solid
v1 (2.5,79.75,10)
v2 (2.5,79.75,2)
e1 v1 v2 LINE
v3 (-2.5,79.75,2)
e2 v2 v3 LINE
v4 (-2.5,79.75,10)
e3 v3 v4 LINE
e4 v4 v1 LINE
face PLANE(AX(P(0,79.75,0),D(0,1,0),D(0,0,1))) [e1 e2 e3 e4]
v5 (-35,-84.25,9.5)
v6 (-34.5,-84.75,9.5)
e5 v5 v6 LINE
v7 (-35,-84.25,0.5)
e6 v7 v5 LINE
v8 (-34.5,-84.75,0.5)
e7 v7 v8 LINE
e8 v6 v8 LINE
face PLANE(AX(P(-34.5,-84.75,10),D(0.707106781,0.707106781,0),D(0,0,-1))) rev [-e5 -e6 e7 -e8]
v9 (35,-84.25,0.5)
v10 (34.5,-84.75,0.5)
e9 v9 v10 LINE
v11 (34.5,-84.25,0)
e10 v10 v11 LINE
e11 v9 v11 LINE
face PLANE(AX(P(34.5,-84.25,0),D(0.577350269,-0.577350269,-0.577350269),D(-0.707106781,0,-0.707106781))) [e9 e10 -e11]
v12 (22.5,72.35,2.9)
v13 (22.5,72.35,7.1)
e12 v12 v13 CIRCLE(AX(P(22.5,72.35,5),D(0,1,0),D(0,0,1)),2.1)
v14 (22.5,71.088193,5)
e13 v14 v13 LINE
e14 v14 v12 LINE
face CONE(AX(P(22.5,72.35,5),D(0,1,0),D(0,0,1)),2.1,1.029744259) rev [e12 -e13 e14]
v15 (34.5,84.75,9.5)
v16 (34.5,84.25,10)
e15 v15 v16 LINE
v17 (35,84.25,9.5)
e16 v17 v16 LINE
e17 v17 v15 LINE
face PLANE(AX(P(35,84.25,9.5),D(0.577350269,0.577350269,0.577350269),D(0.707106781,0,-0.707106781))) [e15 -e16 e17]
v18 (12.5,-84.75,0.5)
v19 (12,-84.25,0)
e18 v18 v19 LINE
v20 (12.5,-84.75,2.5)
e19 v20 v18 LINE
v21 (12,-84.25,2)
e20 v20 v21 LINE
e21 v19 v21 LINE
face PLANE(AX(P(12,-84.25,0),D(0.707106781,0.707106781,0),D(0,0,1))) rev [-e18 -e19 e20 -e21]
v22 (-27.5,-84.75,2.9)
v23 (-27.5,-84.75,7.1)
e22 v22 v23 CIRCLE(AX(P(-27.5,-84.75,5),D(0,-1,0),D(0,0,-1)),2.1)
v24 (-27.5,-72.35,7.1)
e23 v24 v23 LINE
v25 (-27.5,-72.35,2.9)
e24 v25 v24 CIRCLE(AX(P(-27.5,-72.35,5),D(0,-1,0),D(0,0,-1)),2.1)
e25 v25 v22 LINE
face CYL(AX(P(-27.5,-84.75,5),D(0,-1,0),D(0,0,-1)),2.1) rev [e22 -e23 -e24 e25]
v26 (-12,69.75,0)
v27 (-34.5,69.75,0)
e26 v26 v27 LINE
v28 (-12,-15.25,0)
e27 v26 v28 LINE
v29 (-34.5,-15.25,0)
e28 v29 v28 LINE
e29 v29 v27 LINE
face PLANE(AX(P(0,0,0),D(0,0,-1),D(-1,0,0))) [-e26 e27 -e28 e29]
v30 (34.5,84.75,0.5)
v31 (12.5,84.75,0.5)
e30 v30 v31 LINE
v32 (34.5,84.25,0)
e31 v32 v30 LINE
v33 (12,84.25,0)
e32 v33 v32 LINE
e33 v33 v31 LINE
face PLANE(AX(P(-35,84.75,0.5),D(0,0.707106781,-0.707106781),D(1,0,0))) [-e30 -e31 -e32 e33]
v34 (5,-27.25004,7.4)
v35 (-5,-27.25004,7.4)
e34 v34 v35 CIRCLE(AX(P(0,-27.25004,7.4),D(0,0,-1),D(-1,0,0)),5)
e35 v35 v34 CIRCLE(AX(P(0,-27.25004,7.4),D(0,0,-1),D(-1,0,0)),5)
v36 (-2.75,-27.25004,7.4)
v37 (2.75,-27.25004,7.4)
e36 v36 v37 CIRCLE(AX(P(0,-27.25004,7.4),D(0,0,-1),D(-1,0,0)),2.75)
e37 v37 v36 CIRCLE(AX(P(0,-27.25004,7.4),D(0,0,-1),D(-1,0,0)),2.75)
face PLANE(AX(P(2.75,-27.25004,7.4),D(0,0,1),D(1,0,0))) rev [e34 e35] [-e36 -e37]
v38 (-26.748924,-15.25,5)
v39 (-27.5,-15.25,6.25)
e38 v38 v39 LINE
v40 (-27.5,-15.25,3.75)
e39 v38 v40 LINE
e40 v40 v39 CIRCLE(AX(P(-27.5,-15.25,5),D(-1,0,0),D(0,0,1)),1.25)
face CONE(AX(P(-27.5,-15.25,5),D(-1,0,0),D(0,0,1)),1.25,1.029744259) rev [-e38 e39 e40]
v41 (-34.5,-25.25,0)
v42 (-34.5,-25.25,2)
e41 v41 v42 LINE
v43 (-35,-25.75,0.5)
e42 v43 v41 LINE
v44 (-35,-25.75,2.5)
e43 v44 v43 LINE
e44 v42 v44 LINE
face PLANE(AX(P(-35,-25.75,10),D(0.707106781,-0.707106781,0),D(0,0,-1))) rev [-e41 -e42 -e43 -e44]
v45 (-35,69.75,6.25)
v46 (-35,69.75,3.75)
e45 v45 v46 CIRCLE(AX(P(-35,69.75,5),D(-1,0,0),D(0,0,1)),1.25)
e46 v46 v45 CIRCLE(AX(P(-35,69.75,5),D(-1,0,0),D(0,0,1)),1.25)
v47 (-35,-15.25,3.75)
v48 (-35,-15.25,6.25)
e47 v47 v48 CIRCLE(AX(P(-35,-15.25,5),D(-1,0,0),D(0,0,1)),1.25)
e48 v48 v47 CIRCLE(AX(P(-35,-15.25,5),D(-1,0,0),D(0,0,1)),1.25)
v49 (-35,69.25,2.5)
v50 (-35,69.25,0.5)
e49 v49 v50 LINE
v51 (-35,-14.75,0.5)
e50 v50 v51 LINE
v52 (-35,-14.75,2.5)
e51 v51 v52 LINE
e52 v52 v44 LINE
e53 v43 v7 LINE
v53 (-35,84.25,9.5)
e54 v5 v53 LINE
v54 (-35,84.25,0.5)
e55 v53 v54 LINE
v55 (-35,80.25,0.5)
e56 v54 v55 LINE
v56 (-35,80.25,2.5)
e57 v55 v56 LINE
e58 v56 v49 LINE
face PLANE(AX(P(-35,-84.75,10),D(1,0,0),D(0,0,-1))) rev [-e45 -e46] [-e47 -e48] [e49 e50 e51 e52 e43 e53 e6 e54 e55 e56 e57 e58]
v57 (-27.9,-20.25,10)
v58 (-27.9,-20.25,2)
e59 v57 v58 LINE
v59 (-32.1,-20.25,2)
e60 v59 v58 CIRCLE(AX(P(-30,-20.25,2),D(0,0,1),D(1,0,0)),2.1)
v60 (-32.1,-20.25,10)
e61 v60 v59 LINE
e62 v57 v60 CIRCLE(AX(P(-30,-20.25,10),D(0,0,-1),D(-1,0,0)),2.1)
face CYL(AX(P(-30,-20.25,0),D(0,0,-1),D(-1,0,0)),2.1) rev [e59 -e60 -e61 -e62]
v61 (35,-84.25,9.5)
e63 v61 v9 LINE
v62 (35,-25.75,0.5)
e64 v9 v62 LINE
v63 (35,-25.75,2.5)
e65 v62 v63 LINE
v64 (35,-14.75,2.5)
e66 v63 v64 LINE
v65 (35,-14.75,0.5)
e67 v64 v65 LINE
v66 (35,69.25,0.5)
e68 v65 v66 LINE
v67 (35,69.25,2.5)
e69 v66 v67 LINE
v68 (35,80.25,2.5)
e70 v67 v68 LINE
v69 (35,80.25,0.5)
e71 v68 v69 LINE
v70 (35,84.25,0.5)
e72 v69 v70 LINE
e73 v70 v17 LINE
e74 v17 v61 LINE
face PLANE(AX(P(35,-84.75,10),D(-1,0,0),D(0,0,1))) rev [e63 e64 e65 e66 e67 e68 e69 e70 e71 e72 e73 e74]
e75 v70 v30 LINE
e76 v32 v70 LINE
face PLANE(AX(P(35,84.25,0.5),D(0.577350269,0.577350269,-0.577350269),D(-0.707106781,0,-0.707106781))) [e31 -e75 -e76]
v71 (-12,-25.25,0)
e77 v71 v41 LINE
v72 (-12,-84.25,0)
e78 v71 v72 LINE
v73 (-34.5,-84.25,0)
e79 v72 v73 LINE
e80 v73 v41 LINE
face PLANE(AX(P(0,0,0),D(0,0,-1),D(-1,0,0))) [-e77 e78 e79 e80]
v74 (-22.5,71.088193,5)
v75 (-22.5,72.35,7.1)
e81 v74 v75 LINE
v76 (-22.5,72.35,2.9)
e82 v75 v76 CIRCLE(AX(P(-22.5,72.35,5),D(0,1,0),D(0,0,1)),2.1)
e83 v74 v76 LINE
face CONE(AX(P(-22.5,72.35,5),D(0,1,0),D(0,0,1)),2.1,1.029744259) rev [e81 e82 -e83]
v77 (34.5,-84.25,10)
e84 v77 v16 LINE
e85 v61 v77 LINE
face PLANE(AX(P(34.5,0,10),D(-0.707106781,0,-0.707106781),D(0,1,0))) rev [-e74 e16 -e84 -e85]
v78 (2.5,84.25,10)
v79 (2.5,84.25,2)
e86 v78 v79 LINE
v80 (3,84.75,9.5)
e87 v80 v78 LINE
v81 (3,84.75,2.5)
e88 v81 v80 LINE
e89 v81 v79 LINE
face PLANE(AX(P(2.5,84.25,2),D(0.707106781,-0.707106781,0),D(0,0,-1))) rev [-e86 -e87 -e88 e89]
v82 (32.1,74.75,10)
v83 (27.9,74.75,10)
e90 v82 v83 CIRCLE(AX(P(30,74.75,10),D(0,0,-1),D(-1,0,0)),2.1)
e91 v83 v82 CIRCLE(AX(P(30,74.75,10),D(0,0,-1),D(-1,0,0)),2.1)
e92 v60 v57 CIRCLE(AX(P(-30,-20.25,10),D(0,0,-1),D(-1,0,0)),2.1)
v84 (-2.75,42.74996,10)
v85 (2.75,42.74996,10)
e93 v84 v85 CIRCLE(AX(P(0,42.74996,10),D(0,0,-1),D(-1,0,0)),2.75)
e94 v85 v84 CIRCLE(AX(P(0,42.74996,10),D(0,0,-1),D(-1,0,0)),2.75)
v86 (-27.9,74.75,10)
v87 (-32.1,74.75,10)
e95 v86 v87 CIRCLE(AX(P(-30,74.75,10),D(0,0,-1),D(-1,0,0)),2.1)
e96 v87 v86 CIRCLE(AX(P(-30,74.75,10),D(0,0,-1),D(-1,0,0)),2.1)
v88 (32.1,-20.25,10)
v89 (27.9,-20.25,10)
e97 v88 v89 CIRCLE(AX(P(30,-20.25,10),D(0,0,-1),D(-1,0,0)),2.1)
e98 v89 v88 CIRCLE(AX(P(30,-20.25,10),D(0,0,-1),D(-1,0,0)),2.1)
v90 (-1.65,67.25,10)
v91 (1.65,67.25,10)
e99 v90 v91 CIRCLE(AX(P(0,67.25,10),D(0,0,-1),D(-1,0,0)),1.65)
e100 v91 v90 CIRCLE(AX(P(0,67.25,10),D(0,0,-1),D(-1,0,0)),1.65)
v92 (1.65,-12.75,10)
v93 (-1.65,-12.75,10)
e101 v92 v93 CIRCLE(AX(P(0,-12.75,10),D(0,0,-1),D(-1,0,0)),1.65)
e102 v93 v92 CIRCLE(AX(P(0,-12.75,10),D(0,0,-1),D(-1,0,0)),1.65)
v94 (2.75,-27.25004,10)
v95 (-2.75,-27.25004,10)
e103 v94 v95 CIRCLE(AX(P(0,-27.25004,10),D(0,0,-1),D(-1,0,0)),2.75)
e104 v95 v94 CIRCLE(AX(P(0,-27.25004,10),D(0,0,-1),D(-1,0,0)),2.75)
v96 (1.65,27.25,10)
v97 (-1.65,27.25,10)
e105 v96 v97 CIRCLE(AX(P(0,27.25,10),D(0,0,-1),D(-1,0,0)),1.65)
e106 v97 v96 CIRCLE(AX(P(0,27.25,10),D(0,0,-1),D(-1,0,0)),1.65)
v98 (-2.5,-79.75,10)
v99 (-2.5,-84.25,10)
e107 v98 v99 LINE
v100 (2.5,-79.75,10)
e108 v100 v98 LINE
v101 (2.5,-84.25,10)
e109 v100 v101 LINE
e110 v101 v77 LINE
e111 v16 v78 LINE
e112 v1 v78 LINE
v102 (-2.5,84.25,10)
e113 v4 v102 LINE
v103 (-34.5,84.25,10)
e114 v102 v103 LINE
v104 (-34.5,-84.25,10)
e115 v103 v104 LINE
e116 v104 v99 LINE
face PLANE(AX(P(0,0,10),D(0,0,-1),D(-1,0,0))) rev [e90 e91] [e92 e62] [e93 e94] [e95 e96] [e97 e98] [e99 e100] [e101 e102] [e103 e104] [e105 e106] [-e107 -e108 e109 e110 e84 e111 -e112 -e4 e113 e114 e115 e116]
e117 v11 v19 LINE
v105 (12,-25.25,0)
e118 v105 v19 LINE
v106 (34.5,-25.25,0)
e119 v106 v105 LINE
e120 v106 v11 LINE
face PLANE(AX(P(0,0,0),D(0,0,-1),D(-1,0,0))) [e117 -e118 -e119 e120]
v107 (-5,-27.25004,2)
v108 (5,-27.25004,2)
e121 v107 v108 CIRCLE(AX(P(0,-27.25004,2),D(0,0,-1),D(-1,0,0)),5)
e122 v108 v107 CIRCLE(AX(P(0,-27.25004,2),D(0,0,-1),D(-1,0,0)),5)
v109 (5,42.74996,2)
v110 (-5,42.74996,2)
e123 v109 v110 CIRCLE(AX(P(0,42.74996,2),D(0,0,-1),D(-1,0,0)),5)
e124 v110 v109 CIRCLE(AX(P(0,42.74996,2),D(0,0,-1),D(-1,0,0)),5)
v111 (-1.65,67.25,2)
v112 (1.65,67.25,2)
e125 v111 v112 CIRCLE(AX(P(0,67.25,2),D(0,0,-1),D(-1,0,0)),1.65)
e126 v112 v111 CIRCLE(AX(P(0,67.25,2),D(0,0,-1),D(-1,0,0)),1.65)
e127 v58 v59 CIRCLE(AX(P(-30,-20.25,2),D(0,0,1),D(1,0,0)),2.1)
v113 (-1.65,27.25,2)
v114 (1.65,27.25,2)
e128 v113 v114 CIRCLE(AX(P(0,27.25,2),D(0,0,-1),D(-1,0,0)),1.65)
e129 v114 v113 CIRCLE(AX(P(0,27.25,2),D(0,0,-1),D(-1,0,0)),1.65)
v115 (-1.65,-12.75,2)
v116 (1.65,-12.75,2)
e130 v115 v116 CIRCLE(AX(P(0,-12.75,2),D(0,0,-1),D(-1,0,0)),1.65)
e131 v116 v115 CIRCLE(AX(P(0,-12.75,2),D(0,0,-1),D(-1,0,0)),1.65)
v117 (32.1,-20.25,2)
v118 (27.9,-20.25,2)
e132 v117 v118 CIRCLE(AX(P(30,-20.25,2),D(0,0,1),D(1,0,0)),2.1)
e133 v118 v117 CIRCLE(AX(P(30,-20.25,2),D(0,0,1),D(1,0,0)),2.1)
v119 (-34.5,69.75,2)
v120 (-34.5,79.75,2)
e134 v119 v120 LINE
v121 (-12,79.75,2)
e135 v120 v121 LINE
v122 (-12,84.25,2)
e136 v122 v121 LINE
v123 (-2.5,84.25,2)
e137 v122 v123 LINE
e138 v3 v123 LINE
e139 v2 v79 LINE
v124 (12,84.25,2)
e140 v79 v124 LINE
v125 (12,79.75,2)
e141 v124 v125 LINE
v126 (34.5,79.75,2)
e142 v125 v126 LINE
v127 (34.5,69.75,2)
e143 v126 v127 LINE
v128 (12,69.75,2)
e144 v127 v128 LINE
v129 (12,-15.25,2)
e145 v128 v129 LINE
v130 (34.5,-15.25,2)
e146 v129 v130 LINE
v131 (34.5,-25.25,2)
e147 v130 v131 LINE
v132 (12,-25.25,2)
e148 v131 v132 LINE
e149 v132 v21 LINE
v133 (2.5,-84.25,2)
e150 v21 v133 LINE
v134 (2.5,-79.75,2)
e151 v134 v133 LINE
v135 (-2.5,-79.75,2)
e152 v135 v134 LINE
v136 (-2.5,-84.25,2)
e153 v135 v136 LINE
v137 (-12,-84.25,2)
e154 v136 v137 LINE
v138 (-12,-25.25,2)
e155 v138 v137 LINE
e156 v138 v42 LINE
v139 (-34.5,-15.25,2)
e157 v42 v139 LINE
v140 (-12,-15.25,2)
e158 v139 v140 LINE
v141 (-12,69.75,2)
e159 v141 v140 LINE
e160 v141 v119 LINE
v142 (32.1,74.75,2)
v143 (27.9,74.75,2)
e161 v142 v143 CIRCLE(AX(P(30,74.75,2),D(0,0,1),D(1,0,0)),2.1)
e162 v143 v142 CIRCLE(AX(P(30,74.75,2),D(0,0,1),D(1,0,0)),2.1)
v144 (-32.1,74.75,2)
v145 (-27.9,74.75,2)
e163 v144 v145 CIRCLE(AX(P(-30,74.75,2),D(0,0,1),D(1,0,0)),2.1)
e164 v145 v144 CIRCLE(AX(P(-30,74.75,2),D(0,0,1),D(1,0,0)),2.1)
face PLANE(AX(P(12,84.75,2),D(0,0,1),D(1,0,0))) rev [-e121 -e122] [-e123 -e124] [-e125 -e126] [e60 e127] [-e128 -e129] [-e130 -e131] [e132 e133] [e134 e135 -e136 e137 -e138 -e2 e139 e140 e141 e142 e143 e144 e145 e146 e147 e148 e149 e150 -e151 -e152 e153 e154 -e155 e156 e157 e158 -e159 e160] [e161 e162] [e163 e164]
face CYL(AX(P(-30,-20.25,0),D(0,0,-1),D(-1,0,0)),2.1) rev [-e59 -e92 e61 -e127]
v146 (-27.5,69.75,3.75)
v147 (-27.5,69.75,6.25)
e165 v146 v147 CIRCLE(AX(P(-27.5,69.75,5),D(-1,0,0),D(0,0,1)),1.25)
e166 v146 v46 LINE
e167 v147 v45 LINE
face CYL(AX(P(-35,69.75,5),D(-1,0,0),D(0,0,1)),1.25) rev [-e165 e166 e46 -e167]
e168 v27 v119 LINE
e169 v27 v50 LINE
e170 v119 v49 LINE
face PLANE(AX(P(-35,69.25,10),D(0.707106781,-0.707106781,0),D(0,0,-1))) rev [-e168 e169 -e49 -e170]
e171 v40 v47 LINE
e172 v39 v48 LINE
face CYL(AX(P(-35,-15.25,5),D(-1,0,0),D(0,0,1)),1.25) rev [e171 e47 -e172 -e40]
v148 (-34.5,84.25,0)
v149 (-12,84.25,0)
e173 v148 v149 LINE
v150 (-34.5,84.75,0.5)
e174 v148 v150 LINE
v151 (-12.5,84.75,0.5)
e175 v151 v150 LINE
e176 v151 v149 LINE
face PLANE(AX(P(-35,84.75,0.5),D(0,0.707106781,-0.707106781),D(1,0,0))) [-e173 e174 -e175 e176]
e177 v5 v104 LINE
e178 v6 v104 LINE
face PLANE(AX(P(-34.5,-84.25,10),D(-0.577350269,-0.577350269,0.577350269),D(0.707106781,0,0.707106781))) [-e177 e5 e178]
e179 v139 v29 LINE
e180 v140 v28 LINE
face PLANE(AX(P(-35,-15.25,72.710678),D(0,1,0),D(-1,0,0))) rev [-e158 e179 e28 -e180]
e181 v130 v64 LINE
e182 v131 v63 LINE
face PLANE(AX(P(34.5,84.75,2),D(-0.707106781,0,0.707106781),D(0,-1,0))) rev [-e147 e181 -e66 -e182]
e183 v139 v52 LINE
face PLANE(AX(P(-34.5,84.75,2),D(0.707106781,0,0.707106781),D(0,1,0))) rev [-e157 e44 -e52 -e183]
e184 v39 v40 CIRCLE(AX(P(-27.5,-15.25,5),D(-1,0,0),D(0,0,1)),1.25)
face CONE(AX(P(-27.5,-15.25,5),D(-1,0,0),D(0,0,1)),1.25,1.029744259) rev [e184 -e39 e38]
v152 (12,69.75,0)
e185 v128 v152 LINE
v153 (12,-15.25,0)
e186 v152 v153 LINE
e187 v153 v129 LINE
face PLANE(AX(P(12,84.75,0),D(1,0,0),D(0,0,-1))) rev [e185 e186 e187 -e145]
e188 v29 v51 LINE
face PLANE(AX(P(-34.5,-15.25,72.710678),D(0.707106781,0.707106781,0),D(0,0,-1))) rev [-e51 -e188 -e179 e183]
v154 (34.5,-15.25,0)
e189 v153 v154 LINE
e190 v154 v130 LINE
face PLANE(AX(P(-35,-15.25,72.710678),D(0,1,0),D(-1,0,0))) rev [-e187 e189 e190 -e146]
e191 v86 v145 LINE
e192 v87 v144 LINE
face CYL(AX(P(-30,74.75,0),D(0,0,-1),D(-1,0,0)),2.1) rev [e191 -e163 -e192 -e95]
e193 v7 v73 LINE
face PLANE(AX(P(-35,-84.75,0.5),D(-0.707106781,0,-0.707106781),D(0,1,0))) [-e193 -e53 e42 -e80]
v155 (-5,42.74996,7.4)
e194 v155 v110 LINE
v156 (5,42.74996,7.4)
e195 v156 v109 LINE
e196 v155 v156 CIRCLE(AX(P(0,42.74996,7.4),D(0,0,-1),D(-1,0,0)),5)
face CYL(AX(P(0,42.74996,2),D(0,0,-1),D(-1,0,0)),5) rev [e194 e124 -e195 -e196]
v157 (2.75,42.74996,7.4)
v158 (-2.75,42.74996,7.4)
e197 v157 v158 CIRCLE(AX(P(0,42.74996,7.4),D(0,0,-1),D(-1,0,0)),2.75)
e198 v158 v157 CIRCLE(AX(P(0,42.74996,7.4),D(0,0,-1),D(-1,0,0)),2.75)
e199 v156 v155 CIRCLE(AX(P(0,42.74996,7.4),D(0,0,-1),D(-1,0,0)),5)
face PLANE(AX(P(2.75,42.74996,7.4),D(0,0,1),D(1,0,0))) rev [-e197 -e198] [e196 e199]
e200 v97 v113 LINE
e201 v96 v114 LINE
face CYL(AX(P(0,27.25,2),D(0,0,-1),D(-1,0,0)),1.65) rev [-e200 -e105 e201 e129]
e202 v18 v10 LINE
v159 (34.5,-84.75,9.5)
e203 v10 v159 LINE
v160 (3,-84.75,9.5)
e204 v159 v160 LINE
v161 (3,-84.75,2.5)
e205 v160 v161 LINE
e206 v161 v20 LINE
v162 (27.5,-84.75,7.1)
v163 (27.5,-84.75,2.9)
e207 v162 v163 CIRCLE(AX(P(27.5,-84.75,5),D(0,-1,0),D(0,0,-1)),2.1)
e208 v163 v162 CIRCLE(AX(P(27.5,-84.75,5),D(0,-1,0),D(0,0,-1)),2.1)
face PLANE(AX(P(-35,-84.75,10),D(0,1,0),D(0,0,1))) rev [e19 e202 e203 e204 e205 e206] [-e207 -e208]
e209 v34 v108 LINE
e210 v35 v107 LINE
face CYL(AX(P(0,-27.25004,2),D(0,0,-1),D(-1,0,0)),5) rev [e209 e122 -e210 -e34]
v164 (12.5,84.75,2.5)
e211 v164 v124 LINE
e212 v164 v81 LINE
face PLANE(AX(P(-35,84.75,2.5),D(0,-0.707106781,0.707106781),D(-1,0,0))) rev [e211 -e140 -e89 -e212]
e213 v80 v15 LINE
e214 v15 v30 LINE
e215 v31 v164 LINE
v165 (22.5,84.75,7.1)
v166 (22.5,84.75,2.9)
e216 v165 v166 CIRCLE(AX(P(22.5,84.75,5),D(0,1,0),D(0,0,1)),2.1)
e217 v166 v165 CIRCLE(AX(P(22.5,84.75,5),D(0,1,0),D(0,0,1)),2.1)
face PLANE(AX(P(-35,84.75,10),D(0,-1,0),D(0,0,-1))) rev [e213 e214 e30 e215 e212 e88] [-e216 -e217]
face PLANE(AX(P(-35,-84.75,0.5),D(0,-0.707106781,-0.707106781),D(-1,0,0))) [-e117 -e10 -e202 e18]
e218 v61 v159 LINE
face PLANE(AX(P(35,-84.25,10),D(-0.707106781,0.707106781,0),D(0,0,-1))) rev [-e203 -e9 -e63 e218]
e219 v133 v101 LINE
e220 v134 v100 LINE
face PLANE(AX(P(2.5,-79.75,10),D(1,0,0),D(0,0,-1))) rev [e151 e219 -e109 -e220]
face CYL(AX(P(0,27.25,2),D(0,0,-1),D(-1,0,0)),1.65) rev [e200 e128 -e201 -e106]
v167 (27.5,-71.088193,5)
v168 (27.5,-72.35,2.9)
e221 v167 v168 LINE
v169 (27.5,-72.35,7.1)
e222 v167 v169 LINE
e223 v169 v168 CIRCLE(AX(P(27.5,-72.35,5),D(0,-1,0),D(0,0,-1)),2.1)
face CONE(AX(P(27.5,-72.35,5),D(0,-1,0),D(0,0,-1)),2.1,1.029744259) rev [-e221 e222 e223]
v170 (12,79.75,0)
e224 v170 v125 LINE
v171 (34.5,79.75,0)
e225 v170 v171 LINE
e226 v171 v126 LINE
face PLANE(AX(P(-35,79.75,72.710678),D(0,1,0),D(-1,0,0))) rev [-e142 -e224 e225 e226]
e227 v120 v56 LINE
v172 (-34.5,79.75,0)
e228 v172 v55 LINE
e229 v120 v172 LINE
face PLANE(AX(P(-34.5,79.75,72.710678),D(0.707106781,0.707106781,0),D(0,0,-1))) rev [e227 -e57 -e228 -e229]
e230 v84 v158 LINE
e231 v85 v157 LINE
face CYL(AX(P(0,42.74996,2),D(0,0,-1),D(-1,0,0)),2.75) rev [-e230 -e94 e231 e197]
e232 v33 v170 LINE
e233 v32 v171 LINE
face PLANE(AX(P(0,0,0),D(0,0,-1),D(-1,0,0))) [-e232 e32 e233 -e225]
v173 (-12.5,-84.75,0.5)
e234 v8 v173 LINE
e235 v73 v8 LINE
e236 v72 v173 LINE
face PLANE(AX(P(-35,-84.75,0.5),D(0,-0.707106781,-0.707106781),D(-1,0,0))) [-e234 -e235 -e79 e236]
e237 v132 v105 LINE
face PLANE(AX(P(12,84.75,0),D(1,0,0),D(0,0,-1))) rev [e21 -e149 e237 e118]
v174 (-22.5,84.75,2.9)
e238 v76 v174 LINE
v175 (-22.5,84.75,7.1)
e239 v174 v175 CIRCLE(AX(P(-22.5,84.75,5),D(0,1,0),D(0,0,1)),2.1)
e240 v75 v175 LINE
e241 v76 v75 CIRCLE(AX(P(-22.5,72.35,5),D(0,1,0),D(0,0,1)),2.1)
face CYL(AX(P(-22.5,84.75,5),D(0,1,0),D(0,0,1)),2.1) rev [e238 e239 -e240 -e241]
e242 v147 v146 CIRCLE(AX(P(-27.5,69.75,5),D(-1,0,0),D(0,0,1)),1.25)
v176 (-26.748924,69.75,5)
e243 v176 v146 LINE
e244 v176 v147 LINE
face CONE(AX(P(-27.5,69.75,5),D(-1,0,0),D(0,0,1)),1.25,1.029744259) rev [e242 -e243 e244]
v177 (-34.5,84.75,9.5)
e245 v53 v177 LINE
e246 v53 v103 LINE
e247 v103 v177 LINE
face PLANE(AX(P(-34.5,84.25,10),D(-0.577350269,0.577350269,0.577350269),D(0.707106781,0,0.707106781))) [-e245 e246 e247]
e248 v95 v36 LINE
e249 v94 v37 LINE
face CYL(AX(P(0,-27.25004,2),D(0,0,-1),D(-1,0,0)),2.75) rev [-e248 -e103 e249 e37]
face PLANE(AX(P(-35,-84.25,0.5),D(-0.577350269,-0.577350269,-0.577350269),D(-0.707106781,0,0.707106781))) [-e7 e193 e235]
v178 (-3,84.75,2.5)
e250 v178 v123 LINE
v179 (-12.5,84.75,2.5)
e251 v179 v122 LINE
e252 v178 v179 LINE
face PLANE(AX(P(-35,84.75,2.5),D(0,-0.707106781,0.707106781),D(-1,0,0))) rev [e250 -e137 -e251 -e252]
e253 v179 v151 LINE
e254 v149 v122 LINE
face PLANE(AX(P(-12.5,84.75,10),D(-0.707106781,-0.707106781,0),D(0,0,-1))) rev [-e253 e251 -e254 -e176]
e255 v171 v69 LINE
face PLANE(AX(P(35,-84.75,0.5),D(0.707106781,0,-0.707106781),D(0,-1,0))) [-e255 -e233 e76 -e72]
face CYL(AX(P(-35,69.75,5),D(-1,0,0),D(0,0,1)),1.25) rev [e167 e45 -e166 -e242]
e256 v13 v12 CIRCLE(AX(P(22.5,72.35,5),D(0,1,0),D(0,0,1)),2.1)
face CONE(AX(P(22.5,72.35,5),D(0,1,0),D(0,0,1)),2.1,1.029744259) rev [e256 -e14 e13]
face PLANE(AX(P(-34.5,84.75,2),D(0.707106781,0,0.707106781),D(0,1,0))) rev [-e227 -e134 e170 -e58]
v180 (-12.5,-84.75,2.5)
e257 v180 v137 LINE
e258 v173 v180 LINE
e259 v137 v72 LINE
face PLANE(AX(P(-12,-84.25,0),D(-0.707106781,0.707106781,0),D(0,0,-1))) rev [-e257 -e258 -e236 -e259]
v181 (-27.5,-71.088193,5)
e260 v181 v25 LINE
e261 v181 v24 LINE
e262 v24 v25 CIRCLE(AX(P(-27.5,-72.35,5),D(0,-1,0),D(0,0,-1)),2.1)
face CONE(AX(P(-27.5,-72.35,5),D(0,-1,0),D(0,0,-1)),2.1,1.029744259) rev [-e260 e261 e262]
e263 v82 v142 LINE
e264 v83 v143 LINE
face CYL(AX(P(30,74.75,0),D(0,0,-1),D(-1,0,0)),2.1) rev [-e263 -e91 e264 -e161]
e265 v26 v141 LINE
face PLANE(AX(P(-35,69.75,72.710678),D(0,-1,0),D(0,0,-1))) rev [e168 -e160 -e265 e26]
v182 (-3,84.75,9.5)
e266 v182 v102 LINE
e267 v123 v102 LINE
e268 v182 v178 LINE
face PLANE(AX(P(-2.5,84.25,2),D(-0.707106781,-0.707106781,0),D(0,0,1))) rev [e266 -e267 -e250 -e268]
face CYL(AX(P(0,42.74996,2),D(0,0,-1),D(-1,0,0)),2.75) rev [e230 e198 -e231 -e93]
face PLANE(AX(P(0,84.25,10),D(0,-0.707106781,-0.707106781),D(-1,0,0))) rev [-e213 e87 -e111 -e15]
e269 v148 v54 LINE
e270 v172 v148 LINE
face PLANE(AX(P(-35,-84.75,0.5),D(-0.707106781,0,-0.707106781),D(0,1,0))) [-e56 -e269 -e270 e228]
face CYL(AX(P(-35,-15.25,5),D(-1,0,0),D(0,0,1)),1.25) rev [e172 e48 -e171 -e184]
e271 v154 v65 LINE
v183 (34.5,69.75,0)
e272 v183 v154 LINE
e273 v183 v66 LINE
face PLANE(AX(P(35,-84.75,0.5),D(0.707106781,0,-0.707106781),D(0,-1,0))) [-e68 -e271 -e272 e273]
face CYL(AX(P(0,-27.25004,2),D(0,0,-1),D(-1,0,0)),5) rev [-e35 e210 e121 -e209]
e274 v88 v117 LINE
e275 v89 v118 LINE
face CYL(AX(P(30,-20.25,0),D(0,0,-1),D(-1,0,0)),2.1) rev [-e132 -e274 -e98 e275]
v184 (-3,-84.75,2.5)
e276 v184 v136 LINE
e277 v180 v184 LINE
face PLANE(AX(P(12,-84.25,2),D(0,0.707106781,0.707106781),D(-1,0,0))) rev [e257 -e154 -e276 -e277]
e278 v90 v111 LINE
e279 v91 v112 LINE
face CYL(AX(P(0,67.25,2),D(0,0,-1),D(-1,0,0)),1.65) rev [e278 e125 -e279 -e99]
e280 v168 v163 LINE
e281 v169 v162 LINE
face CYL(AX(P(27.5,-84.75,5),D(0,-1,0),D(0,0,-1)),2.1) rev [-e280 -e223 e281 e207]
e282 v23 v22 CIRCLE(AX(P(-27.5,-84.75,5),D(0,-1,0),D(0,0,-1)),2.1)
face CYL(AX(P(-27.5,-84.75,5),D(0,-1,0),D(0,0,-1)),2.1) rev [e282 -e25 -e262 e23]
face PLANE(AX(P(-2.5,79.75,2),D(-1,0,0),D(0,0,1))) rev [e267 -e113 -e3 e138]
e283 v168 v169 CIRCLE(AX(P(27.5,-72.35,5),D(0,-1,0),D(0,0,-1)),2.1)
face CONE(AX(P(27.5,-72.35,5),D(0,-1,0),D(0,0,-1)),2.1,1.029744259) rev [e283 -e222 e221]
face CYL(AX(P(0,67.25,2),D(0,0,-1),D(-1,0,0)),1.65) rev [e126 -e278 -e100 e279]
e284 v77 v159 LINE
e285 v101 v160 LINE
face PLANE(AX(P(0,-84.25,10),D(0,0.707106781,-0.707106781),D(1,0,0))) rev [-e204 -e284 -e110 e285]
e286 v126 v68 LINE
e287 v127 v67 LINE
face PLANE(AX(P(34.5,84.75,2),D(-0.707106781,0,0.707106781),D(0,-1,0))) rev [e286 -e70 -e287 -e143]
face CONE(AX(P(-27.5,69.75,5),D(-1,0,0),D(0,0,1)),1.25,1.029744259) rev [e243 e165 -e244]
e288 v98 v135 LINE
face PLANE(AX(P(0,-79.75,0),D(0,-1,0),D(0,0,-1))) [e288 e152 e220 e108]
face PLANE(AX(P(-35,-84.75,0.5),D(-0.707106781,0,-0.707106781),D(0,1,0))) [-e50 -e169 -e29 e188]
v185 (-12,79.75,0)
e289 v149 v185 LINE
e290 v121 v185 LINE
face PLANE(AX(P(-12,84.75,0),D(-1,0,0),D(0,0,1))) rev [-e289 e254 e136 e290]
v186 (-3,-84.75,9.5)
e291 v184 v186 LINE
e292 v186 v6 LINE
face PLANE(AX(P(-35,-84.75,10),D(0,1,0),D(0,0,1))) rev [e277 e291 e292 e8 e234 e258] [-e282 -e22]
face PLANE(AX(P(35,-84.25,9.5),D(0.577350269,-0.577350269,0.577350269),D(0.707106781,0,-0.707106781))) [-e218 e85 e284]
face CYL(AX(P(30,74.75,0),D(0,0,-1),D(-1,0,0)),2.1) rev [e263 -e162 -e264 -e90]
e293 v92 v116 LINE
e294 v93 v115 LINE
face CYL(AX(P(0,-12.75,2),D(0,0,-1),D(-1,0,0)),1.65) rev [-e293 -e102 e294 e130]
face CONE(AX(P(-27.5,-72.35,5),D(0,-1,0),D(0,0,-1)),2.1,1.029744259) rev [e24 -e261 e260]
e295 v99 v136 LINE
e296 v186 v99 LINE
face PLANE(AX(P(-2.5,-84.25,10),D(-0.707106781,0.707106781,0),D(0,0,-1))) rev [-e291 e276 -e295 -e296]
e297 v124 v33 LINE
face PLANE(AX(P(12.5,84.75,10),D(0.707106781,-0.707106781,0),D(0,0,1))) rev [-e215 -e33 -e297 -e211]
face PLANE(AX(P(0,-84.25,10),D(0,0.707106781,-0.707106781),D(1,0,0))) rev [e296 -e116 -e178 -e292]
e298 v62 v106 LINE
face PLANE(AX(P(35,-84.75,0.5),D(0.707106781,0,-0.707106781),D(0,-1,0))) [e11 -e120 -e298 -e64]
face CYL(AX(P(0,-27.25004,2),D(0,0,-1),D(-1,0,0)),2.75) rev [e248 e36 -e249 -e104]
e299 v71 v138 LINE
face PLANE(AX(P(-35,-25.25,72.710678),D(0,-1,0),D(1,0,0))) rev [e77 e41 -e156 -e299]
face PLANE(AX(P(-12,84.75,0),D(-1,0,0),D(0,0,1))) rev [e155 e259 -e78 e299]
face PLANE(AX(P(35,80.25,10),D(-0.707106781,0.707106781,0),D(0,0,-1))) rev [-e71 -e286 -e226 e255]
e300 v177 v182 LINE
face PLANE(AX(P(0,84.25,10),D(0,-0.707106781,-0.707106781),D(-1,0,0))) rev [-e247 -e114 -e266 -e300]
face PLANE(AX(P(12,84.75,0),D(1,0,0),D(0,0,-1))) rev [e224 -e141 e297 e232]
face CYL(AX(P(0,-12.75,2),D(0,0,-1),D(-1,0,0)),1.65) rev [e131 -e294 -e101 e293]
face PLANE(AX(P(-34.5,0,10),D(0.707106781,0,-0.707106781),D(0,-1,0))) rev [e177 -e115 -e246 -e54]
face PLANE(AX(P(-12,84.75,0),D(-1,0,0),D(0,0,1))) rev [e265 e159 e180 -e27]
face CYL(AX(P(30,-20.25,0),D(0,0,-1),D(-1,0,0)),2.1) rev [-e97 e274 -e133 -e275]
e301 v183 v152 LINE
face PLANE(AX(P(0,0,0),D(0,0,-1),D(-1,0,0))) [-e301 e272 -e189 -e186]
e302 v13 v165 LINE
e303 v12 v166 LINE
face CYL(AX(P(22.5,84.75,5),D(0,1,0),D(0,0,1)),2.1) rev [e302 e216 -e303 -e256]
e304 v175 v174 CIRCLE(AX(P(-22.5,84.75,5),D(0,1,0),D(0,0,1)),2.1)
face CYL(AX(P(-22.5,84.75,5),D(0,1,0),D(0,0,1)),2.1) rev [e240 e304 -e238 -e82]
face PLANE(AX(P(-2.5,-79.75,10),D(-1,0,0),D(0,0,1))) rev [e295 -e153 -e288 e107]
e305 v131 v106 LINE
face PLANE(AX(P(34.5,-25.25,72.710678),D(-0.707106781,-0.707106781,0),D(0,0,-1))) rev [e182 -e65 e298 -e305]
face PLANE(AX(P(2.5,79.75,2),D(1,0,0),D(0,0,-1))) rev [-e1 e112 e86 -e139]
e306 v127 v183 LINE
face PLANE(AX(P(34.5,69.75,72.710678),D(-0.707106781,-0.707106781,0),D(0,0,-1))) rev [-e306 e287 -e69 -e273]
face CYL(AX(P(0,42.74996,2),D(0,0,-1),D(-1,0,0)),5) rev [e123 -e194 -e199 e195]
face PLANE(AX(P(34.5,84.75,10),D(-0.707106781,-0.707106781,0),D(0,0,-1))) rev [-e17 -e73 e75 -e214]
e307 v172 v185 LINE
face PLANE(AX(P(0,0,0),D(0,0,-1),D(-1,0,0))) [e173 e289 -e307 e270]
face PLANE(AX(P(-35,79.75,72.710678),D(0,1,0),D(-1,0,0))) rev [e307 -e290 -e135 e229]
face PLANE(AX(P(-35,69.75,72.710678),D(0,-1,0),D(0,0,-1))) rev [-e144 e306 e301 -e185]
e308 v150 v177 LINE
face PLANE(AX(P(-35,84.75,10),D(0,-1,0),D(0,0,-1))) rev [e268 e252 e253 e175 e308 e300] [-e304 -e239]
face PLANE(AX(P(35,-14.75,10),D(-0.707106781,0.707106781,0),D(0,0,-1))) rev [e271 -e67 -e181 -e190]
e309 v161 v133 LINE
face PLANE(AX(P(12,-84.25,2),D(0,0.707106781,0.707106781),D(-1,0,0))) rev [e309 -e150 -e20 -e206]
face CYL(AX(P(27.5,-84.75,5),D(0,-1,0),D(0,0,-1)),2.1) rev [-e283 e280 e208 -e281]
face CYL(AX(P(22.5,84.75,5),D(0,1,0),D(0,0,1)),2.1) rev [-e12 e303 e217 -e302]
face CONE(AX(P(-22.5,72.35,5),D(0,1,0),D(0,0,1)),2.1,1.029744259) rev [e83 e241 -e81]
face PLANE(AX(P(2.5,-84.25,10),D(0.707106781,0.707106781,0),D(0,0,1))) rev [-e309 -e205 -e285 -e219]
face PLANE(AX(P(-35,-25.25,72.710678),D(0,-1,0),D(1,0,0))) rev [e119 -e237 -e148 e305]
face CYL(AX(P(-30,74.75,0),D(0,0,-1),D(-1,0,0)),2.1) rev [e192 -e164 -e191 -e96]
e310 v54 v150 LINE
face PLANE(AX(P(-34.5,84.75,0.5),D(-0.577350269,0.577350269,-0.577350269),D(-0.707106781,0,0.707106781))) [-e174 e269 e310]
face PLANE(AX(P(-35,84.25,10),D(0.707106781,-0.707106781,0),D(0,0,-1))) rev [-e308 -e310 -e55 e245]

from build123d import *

# Parameters (mm, degrees)
SKETCH_1_W                     = 70
SKETCH_1_H                     = 169.5
EXTRUDE_1_DEPTH                = 10
SKETCH_2_W                     = 24
SKETCH_2_H                     = 2
CUT_EXTRUDE_1_DEPTH            = 174.364500403
SKETCH_3_W                     = 70
SKETCH_3_H                     = 10
CUT_EXTRUDE_2_DEPTH            = 2
SKETCH_4_W                     = 70
SKETCH_4_H                     = 10
CUT_EXTRUDE_3_DEPTH            = 2
HOLE_WIZARD_M5_1_D             = 4.2
HOLE_WIZARD_M4_1_D             = 3.3
HOLE_WIZARD_M5_2_D             = 4.2
HOLE_WIZARD_M5_2_DEPTH         = 12.4
HOLE_WIZARD_M5_2_TIP           = 1.2618073
SKETCH_11_W                    = 5
SKETCH_11_H                    = 8
CUT_EXTRUDE_4_DEPTH            = 5
HOLE_WIZARD_M5_3_D             = 4.2
HOLE_WIZARD_M5_3_DEPTH         = 12.4
HOLE_WIZARD_M5_3_TIP           = 1.2618073
SKETCH_14_W                    = 5
SKETCH_14_H                    = 8
CUT_EXTRUDE_5_DEPTH            = 5
HOLE_WIZARD_M5_1_2_D           = 5.5
HOLE_WIZARD_M5_1_2_DEPTH       = 12.4
HOLE_WIZARD_M5_1_2_CBORE_D     = 10
HOLE_WIZARD_M5_1_2_CBORE_DEPTH = 5.4
HOLE_WIZARD_M5_1_2_TIP         = 1.652366702
HOLE_WIZARD_M3_1_D             = 2.5
HOLE_WIZARD_M3_1_DEPTH         = 7.5
HOLE_WIZARD_M3_1_TIP           = 0.751075774
CHAMFER_1_SIZE                 = 0.5


with BuildPart() as part:
    # 草图1 → 凸台-拉伸1 (new body)
    with BuildSketch(Plane.XY):
        Rectangle(SKETCH_1_W, SKETCH_1_H)
    extrude(amount=EXTRUDE_1_DEPTH)

    # 草图2 → 切除-拉伸1 (cut, through all)
    with BuildSketch(Plane.XZ.offset(84.75)):
        with Locations((0, 1)):
            Rectangle(SKETCH_2_W, SKETCH_2_H)
    extrude(amount=-CUT_EXTRUDE_1_DEPTH, mode=Mode.SUBTRACT)

    # 草图3 → 切除-拉伸2 (cut)
    with BuildSketch(Plane(origin=(0, 0, 0), x_dir=(-1, 0, 0), z_dir=(0, 0, -1))):
        with Locations((0, 74.75)):
            Rectangle(SKETCH_3_W, SKETCH_3_H)
    extrude(amount=-CUT_EXTRUDE_2_DEPTH, mode=Mode.SUBTRACT)

    # 草图4 → 切除-拉伸3 (cut)
    with BuildSketch(Plane(origin=(0, 0, 0), x_dir=(-1, 0, 0), z_dir=(0, 0, -1))):
        with Locations((0, -20.25)):
            Rectangle(SKETCH_4_W, SKETCH_4_H)
    extrude(amount=-CUT_EXTRUDE_3_DEPTH, mode=Mode.SUBTRACT)

    # Hole Wizard M5 _1 (through all)
    with Locations(Plane(origin=(0, 0, 0), x_dir=(-1, 0, 0), z_dir=(0, 0, -1))):
        with Locations((-30, -20.25), (30, -20.25), (-30, 74.75), (30, 74.75)):
            Hole(HOLE_WIZARD_M5_1_D / 2)

    # M4 螺纹孔1 (through all)
    with Locations(Plane(origin=(0, 0, 2), x_dir=(-1, 0, 0), z_dir=(0, 0, -1))):
        with Locations((0, -12.75), (0, 27.25), (0, 67.25)):
            Hole(HOLE_WIZARD_M4_1_D / 2)

    # M5 螺纹孔2
    with Locations(Plane(origin=(0, -84.75, 0), x_dir=(-1, 0, 0), z_dir=(0, -1, 0))):
        with Locations((-27.5, -5), (27.5, -5)):
            Hole(HOLE_WIZARD_M5_2_D / 2, depth=HOLE_WIZARD_M5_2_DEPTH)
            with Locations((0, 0, -(HOLE_WIZARD_M5_2_DEPTH + HOLE_WIZARD_M5_2_TIP / 2))):  # 118° drill point
                Cone(0, HOLE_WIZARD_M5_2_D / 2, HOLE_WIZARD_M5_2_TIP, mode=Mode.SUBTRACT)

    # 草图11 → 切除-拉伸4 (cut)
    with BuildSketch(Plane.XZ.offset(84.75)):
        with Locations((0, 6)):
            Rectangle(SKETCH_11_W, SKETCH_11_H)
    extrude(amount=-CUT_EXTRUDE_4_DEPTH, mode=Mode.SUBTRACT)

    # M5 螺纹孔3
    with Locations(Plane(origin=(0, 84.75, 0), x_dir=(1, 0, 0), z_dir=(0, 1, 0))):
        with Locations((22.5, -5), (-22.5, -5)):
            Hole(HOLE_WIZARD_M5_3_D / 2, depth=HOLE_WIZARD_M5_3_DEPTH)
            with Locations((0, 0, -(HOLE_WIZARD_M5_3_DEPTH + HOLE_WIZARD_M5_3_TIP / 2))):  # 118° drill point
                Cone(0, HOLE_WIZARD_M5_3_D / 2, HOLE_WIZARD_M5_3_TIP, mode=Mode.SUBTRACT)

    # 草图14 → 切除-拉伸5 (cut)
    with BuildSketch(Plane(origin=(0, 84.75, 0), x_dir=(1, 0, 0), z_dir=(0, 1, 0))):
        with Locations((0, -6)):
            Rectangle(SKETCH_14_W, SKETCH_14_H)
    extrude(amount=-CUT_EXTRUDE_5_DEPTH, mode=Mode.SUBTRACT)

    # Hole Wizard M5 _1 2
    with Locations(Plane(origin=(0, 0, 2), x_dir=(-1, 0, 0), z_dir=(0, 0, -1))):
        with Locations((0, -27.250039646), (0, 42.749960354)):
            CounterBoreHole(HOLE_WIZARD_M5_1_2_D / 2, HOLE_WIZARD_M5_1_2_CBORE_D / 2, HOLE_WIZARD_M5_1_2_CBORE_DEPTH, depth=HOLE_WIZARD_M5_1_2_DEPTH)
            with Locations((0, 0, -(HOLE_WIZARD_M5_1_2_DEPTH + HOLE_WIZARD_M5_1_2_TIP / 2))):  # 118° drill point
                Cone(0, HOLE_WIZARD_M5_1_2_D / 2, HOLE_WIZARD_M5_1_2_TIP, mode=Mode.SUBTRACT)

    # M3 螺纹孔1
    with Locations(Plane.ZY.offset(35)):
        with Locations((5, -15.25), (5, 69.75)):
            Hole(HOLE_WIZARD_M3_1_D / 2, depth=HOLE_WIZARD_M3_1_DEPTH)
            with Locations((0, 0, -(HOLE_WIZARD_M3_1_DEPTH + HOLE_WIZARD_M3_1_TIP / 2))):  # 118° drill point
                Cone(0, HOLE_WIZARD_M3_1_D / 2, HOLE_WIZARD_M3_1_TIP, mode=Mode.SUBTRACT)

    # 倒角1
    chamfer_1_edges = [part.edges().sort_by_distance(p)[0] for p in [
        (-35, 0, 10),
        (23.5, -84.75, 0),
        (-7.25, -84.75, 2),
        (18.75, -84.75, 10),
        (-23.5, 84.75, 0),
        (-2.5, -84.75, 6),
        (2.5, -84.75, 6),
        (-18.75, -84.75, 10),
        (-7.25, 84.75, 2),
        (-18.75, 84.75, 10),
        (-2.5, 84.75, 6),
        (2.5, 84.75, 6),
        (12, 84.75, 1),
        (-12, 84.75, 1),
        (7.25, 84.75, 2),
        (12, -84.75, 1),
        (7.25, -84.75, 2),
        (-12, -84.75, 1),
        (-35, 27.25, 0),
        (35, 82.25, 0),
        (35, 79.75, 1),
        (-35, 69.75, 1),
        (35, 74.75, 2),
        (35, 69.75, 1),
        (-35, 74.75, 2),
        (-35, 79.75, 1),
        (35, 0, 10),
        (-23.5, -84.75, 0),
        (-35, 82.25, 0),
        (23.5, 84.75, 0),
        (35, -55, 0),
        (-35, -55, 0),
        (35, 27.25, 0),
        (35, -15.25, 1),
        (-35, -25.25, 1),
        (35, -20.25, 2),
        (35, -25.25, 1),
        (-35, -20.25, 2),
        (-35, -15.25, 1),
        (35, -84.75, 5),
        (-35, -84.75, 5),
        (-35, 84.75, 5),
        (35, 84.75, 5),
        (18.75, 84.75, 10),
    ]]
    chamfer(chamfer_1_edges, length=CHAMFER_1_SIZE)


solid = part.part
